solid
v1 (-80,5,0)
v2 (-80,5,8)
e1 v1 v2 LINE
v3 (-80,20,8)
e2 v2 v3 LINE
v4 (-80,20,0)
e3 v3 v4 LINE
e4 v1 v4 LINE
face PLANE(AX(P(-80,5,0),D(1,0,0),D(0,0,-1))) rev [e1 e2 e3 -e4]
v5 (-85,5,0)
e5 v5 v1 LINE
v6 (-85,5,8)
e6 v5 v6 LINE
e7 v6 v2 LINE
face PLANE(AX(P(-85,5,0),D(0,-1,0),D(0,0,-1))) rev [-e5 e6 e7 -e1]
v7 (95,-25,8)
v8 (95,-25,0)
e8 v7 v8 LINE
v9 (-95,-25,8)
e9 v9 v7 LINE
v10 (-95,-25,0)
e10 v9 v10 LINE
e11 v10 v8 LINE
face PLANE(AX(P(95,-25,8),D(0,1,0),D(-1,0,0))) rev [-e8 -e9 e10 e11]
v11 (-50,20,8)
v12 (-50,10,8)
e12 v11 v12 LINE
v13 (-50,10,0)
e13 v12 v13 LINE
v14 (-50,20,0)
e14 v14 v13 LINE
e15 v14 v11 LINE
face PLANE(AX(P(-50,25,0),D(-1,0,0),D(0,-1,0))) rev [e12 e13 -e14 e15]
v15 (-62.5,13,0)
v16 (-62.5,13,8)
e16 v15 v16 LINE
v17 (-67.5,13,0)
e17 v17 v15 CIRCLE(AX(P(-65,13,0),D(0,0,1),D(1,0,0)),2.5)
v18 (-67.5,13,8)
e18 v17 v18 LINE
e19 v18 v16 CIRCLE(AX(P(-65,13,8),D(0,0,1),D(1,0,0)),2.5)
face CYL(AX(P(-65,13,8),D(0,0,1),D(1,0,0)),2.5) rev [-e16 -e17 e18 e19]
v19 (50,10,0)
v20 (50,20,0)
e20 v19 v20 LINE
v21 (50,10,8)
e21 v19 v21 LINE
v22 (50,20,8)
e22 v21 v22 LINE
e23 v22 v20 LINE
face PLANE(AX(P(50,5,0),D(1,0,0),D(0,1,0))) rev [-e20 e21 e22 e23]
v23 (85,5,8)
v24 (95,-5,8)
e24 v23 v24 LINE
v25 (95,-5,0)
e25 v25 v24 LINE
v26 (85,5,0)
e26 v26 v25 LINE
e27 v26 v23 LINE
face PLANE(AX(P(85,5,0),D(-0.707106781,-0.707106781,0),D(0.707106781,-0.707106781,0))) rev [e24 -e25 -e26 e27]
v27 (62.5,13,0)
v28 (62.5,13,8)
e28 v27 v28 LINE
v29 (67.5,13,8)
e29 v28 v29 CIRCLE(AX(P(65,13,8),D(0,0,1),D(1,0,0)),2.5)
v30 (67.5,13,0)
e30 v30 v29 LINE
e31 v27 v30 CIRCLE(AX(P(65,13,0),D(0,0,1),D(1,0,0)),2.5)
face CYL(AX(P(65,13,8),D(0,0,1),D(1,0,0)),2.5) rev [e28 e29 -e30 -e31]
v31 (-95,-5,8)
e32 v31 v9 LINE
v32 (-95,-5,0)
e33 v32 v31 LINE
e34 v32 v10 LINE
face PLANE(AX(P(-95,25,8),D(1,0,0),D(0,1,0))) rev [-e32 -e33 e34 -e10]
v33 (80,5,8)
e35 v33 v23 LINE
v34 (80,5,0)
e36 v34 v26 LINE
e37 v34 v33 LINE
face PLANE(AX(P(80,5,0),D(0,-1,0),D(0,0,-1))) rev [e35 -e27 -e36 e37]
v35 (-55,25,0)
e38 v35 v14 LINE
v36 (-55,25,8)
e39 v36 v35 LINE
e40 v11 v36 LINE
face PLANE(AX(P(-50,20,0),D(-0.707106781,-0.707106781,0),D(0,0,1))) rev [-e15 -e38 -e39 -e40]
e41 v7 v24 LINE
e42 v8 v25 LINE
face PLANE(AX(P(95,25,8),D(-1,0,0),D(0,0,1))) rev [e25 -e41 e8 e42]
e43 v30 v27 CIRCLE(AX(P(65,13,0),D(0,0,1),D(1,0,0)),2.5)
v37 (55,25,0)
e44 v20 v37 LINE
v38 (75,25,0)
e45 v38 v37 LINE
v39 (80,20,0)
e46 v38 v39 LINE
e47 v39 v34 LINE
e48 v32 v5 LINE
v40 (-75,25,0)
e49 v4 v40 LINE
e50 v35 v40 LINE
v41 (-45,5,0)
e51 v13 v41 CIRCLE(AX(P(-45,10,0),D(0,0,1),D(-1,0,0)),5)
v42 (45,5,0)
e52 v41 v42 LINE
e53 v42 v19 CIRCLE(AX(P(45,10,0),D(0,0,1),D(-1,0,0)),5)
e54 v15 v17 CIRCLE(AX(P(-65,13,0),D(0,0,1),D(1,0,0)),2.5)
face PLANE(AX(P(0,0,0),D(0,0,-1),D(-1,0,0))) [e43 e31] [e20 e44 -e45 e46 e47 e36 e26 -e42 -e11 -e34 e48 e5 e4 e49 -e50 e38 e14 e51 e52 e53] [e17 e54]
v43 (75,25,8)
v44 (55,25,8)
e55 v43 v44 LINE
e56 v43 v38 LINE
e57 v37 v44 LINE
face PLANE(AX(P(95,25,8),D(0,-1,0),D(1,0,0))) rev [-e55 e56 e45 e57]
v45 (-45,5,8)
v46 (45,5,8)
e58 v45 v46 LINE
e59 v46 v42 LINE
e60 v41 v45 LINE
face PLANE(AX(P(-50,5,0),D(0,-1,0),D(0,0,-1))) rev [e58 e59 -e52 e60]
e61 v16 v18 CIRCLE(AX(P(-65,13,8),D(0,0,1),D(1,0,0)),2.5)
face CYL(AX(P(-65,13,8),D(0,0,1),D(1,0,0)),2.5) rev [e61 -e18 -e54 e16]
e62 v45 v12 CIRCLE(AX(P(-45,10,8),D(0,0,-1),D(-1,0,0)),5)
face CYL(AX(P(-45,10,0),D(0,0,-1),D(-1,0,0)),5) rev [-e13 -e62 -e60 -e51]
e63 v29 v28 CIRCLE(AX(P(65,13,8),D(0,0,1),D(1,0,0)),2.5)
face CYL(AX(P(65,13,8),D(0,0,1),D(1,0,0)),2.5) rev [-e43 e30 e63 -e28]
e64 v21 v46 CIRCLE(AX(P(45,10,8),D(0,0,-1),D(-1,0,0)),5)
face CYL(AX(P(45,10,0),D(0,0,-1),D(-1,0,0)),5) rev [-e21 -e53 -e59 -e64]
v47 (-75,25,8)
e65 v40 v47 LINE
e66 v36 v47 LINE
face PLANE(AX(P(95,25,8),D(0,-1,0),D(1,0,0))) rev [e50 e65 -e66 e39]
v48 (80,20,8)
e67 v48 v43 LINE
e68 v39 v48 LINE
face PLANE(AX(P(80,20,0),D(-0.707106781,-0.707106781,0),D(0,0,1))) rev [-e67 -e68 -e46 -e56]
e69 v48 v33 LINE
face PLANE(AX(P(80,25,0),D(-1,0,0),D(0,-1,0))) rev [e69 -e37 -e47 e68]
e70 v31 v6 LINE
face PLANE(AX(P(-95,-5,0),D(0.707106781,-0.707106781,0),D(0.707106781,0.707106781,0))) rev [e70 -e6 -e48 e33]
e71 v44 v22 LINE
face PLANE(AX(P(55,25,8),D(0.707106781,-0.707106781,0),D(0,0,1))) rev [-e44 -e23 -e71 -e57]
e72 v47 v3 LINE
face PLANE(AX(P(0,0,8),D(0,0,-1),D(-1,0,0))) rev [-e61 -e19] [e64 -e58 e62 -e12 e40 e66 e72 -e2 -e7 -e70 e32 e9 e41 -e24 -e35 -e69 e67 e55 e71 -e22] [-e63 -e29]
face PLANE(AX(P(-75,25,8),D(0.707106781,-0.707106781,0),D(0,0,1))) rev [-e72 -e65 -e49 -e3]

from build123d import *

# Parameters (mm, degrees)
SKETCH_1_W          = 190
SKETCH_1_H          = 50
EXTRUDE_1_DEPTH     = 8
CUT_EXTRUDE_1_DEPTH = 8
CHAMFER_1_SIZE      = 5
HOLE_WIZARD_M6_1_D  = 5
FILLET_1_R          = 5


with BuildPart() as part:
    # 草图1 → 凸台-拉伸1 (new body)
    with BuildSketch(Plane.XY):
        Rectangle(SKETCH_1_W, SKETCH_1_H)
    extrude(amount=EXTRUDE_1_DEPTH)

    # 草图2 → 切除-拉伸1 (cut)
    with BuildSketch(Plane.XY.offset(8)):
        Polygon((-95, -5), (-85, 5), (-80, 5), (-80, 25), (-50, 25), (-50, 5), (50, 5), (50, 25), (80, 25), (80, 5), (85, 5), (95, -5), (95, 25), (-3.801071979, 36.264806318), (-95, 25), align=None)
    extrude(amount=-CUT_EXTRUDE_1_DEPTH, mode=Mode.SUBTRACT)

    # 倒角1
    chamfer_1_edges = [part.edges().sort_by_distance(p)[0] for p in [
        (80, 25, 4),
        (50, 25, 4),
        (-50, 25, 4),
        (-80, 25, 4),
    ]]
    chamfer(chamfer_1_edges, length=CHAMFER_1_SIZE)

    # M6 螺纹孔1 (through all)
    with Locations(Plane.XY.offset(8)):
        with Locations((-65, 13), (65, 13)):
            Hole(HOLE_WIZARD_M6_1_D / 2)

    # 圆角1
    fillet_1_edges = [part.edges().sort_by_distance(p)[0] for p in [
        (50, 5, 4),
        (-50, 5, 4),
    ]]
    fillet(fillet_1_edges, radius=FILLET_1_R)


solid = part.part
